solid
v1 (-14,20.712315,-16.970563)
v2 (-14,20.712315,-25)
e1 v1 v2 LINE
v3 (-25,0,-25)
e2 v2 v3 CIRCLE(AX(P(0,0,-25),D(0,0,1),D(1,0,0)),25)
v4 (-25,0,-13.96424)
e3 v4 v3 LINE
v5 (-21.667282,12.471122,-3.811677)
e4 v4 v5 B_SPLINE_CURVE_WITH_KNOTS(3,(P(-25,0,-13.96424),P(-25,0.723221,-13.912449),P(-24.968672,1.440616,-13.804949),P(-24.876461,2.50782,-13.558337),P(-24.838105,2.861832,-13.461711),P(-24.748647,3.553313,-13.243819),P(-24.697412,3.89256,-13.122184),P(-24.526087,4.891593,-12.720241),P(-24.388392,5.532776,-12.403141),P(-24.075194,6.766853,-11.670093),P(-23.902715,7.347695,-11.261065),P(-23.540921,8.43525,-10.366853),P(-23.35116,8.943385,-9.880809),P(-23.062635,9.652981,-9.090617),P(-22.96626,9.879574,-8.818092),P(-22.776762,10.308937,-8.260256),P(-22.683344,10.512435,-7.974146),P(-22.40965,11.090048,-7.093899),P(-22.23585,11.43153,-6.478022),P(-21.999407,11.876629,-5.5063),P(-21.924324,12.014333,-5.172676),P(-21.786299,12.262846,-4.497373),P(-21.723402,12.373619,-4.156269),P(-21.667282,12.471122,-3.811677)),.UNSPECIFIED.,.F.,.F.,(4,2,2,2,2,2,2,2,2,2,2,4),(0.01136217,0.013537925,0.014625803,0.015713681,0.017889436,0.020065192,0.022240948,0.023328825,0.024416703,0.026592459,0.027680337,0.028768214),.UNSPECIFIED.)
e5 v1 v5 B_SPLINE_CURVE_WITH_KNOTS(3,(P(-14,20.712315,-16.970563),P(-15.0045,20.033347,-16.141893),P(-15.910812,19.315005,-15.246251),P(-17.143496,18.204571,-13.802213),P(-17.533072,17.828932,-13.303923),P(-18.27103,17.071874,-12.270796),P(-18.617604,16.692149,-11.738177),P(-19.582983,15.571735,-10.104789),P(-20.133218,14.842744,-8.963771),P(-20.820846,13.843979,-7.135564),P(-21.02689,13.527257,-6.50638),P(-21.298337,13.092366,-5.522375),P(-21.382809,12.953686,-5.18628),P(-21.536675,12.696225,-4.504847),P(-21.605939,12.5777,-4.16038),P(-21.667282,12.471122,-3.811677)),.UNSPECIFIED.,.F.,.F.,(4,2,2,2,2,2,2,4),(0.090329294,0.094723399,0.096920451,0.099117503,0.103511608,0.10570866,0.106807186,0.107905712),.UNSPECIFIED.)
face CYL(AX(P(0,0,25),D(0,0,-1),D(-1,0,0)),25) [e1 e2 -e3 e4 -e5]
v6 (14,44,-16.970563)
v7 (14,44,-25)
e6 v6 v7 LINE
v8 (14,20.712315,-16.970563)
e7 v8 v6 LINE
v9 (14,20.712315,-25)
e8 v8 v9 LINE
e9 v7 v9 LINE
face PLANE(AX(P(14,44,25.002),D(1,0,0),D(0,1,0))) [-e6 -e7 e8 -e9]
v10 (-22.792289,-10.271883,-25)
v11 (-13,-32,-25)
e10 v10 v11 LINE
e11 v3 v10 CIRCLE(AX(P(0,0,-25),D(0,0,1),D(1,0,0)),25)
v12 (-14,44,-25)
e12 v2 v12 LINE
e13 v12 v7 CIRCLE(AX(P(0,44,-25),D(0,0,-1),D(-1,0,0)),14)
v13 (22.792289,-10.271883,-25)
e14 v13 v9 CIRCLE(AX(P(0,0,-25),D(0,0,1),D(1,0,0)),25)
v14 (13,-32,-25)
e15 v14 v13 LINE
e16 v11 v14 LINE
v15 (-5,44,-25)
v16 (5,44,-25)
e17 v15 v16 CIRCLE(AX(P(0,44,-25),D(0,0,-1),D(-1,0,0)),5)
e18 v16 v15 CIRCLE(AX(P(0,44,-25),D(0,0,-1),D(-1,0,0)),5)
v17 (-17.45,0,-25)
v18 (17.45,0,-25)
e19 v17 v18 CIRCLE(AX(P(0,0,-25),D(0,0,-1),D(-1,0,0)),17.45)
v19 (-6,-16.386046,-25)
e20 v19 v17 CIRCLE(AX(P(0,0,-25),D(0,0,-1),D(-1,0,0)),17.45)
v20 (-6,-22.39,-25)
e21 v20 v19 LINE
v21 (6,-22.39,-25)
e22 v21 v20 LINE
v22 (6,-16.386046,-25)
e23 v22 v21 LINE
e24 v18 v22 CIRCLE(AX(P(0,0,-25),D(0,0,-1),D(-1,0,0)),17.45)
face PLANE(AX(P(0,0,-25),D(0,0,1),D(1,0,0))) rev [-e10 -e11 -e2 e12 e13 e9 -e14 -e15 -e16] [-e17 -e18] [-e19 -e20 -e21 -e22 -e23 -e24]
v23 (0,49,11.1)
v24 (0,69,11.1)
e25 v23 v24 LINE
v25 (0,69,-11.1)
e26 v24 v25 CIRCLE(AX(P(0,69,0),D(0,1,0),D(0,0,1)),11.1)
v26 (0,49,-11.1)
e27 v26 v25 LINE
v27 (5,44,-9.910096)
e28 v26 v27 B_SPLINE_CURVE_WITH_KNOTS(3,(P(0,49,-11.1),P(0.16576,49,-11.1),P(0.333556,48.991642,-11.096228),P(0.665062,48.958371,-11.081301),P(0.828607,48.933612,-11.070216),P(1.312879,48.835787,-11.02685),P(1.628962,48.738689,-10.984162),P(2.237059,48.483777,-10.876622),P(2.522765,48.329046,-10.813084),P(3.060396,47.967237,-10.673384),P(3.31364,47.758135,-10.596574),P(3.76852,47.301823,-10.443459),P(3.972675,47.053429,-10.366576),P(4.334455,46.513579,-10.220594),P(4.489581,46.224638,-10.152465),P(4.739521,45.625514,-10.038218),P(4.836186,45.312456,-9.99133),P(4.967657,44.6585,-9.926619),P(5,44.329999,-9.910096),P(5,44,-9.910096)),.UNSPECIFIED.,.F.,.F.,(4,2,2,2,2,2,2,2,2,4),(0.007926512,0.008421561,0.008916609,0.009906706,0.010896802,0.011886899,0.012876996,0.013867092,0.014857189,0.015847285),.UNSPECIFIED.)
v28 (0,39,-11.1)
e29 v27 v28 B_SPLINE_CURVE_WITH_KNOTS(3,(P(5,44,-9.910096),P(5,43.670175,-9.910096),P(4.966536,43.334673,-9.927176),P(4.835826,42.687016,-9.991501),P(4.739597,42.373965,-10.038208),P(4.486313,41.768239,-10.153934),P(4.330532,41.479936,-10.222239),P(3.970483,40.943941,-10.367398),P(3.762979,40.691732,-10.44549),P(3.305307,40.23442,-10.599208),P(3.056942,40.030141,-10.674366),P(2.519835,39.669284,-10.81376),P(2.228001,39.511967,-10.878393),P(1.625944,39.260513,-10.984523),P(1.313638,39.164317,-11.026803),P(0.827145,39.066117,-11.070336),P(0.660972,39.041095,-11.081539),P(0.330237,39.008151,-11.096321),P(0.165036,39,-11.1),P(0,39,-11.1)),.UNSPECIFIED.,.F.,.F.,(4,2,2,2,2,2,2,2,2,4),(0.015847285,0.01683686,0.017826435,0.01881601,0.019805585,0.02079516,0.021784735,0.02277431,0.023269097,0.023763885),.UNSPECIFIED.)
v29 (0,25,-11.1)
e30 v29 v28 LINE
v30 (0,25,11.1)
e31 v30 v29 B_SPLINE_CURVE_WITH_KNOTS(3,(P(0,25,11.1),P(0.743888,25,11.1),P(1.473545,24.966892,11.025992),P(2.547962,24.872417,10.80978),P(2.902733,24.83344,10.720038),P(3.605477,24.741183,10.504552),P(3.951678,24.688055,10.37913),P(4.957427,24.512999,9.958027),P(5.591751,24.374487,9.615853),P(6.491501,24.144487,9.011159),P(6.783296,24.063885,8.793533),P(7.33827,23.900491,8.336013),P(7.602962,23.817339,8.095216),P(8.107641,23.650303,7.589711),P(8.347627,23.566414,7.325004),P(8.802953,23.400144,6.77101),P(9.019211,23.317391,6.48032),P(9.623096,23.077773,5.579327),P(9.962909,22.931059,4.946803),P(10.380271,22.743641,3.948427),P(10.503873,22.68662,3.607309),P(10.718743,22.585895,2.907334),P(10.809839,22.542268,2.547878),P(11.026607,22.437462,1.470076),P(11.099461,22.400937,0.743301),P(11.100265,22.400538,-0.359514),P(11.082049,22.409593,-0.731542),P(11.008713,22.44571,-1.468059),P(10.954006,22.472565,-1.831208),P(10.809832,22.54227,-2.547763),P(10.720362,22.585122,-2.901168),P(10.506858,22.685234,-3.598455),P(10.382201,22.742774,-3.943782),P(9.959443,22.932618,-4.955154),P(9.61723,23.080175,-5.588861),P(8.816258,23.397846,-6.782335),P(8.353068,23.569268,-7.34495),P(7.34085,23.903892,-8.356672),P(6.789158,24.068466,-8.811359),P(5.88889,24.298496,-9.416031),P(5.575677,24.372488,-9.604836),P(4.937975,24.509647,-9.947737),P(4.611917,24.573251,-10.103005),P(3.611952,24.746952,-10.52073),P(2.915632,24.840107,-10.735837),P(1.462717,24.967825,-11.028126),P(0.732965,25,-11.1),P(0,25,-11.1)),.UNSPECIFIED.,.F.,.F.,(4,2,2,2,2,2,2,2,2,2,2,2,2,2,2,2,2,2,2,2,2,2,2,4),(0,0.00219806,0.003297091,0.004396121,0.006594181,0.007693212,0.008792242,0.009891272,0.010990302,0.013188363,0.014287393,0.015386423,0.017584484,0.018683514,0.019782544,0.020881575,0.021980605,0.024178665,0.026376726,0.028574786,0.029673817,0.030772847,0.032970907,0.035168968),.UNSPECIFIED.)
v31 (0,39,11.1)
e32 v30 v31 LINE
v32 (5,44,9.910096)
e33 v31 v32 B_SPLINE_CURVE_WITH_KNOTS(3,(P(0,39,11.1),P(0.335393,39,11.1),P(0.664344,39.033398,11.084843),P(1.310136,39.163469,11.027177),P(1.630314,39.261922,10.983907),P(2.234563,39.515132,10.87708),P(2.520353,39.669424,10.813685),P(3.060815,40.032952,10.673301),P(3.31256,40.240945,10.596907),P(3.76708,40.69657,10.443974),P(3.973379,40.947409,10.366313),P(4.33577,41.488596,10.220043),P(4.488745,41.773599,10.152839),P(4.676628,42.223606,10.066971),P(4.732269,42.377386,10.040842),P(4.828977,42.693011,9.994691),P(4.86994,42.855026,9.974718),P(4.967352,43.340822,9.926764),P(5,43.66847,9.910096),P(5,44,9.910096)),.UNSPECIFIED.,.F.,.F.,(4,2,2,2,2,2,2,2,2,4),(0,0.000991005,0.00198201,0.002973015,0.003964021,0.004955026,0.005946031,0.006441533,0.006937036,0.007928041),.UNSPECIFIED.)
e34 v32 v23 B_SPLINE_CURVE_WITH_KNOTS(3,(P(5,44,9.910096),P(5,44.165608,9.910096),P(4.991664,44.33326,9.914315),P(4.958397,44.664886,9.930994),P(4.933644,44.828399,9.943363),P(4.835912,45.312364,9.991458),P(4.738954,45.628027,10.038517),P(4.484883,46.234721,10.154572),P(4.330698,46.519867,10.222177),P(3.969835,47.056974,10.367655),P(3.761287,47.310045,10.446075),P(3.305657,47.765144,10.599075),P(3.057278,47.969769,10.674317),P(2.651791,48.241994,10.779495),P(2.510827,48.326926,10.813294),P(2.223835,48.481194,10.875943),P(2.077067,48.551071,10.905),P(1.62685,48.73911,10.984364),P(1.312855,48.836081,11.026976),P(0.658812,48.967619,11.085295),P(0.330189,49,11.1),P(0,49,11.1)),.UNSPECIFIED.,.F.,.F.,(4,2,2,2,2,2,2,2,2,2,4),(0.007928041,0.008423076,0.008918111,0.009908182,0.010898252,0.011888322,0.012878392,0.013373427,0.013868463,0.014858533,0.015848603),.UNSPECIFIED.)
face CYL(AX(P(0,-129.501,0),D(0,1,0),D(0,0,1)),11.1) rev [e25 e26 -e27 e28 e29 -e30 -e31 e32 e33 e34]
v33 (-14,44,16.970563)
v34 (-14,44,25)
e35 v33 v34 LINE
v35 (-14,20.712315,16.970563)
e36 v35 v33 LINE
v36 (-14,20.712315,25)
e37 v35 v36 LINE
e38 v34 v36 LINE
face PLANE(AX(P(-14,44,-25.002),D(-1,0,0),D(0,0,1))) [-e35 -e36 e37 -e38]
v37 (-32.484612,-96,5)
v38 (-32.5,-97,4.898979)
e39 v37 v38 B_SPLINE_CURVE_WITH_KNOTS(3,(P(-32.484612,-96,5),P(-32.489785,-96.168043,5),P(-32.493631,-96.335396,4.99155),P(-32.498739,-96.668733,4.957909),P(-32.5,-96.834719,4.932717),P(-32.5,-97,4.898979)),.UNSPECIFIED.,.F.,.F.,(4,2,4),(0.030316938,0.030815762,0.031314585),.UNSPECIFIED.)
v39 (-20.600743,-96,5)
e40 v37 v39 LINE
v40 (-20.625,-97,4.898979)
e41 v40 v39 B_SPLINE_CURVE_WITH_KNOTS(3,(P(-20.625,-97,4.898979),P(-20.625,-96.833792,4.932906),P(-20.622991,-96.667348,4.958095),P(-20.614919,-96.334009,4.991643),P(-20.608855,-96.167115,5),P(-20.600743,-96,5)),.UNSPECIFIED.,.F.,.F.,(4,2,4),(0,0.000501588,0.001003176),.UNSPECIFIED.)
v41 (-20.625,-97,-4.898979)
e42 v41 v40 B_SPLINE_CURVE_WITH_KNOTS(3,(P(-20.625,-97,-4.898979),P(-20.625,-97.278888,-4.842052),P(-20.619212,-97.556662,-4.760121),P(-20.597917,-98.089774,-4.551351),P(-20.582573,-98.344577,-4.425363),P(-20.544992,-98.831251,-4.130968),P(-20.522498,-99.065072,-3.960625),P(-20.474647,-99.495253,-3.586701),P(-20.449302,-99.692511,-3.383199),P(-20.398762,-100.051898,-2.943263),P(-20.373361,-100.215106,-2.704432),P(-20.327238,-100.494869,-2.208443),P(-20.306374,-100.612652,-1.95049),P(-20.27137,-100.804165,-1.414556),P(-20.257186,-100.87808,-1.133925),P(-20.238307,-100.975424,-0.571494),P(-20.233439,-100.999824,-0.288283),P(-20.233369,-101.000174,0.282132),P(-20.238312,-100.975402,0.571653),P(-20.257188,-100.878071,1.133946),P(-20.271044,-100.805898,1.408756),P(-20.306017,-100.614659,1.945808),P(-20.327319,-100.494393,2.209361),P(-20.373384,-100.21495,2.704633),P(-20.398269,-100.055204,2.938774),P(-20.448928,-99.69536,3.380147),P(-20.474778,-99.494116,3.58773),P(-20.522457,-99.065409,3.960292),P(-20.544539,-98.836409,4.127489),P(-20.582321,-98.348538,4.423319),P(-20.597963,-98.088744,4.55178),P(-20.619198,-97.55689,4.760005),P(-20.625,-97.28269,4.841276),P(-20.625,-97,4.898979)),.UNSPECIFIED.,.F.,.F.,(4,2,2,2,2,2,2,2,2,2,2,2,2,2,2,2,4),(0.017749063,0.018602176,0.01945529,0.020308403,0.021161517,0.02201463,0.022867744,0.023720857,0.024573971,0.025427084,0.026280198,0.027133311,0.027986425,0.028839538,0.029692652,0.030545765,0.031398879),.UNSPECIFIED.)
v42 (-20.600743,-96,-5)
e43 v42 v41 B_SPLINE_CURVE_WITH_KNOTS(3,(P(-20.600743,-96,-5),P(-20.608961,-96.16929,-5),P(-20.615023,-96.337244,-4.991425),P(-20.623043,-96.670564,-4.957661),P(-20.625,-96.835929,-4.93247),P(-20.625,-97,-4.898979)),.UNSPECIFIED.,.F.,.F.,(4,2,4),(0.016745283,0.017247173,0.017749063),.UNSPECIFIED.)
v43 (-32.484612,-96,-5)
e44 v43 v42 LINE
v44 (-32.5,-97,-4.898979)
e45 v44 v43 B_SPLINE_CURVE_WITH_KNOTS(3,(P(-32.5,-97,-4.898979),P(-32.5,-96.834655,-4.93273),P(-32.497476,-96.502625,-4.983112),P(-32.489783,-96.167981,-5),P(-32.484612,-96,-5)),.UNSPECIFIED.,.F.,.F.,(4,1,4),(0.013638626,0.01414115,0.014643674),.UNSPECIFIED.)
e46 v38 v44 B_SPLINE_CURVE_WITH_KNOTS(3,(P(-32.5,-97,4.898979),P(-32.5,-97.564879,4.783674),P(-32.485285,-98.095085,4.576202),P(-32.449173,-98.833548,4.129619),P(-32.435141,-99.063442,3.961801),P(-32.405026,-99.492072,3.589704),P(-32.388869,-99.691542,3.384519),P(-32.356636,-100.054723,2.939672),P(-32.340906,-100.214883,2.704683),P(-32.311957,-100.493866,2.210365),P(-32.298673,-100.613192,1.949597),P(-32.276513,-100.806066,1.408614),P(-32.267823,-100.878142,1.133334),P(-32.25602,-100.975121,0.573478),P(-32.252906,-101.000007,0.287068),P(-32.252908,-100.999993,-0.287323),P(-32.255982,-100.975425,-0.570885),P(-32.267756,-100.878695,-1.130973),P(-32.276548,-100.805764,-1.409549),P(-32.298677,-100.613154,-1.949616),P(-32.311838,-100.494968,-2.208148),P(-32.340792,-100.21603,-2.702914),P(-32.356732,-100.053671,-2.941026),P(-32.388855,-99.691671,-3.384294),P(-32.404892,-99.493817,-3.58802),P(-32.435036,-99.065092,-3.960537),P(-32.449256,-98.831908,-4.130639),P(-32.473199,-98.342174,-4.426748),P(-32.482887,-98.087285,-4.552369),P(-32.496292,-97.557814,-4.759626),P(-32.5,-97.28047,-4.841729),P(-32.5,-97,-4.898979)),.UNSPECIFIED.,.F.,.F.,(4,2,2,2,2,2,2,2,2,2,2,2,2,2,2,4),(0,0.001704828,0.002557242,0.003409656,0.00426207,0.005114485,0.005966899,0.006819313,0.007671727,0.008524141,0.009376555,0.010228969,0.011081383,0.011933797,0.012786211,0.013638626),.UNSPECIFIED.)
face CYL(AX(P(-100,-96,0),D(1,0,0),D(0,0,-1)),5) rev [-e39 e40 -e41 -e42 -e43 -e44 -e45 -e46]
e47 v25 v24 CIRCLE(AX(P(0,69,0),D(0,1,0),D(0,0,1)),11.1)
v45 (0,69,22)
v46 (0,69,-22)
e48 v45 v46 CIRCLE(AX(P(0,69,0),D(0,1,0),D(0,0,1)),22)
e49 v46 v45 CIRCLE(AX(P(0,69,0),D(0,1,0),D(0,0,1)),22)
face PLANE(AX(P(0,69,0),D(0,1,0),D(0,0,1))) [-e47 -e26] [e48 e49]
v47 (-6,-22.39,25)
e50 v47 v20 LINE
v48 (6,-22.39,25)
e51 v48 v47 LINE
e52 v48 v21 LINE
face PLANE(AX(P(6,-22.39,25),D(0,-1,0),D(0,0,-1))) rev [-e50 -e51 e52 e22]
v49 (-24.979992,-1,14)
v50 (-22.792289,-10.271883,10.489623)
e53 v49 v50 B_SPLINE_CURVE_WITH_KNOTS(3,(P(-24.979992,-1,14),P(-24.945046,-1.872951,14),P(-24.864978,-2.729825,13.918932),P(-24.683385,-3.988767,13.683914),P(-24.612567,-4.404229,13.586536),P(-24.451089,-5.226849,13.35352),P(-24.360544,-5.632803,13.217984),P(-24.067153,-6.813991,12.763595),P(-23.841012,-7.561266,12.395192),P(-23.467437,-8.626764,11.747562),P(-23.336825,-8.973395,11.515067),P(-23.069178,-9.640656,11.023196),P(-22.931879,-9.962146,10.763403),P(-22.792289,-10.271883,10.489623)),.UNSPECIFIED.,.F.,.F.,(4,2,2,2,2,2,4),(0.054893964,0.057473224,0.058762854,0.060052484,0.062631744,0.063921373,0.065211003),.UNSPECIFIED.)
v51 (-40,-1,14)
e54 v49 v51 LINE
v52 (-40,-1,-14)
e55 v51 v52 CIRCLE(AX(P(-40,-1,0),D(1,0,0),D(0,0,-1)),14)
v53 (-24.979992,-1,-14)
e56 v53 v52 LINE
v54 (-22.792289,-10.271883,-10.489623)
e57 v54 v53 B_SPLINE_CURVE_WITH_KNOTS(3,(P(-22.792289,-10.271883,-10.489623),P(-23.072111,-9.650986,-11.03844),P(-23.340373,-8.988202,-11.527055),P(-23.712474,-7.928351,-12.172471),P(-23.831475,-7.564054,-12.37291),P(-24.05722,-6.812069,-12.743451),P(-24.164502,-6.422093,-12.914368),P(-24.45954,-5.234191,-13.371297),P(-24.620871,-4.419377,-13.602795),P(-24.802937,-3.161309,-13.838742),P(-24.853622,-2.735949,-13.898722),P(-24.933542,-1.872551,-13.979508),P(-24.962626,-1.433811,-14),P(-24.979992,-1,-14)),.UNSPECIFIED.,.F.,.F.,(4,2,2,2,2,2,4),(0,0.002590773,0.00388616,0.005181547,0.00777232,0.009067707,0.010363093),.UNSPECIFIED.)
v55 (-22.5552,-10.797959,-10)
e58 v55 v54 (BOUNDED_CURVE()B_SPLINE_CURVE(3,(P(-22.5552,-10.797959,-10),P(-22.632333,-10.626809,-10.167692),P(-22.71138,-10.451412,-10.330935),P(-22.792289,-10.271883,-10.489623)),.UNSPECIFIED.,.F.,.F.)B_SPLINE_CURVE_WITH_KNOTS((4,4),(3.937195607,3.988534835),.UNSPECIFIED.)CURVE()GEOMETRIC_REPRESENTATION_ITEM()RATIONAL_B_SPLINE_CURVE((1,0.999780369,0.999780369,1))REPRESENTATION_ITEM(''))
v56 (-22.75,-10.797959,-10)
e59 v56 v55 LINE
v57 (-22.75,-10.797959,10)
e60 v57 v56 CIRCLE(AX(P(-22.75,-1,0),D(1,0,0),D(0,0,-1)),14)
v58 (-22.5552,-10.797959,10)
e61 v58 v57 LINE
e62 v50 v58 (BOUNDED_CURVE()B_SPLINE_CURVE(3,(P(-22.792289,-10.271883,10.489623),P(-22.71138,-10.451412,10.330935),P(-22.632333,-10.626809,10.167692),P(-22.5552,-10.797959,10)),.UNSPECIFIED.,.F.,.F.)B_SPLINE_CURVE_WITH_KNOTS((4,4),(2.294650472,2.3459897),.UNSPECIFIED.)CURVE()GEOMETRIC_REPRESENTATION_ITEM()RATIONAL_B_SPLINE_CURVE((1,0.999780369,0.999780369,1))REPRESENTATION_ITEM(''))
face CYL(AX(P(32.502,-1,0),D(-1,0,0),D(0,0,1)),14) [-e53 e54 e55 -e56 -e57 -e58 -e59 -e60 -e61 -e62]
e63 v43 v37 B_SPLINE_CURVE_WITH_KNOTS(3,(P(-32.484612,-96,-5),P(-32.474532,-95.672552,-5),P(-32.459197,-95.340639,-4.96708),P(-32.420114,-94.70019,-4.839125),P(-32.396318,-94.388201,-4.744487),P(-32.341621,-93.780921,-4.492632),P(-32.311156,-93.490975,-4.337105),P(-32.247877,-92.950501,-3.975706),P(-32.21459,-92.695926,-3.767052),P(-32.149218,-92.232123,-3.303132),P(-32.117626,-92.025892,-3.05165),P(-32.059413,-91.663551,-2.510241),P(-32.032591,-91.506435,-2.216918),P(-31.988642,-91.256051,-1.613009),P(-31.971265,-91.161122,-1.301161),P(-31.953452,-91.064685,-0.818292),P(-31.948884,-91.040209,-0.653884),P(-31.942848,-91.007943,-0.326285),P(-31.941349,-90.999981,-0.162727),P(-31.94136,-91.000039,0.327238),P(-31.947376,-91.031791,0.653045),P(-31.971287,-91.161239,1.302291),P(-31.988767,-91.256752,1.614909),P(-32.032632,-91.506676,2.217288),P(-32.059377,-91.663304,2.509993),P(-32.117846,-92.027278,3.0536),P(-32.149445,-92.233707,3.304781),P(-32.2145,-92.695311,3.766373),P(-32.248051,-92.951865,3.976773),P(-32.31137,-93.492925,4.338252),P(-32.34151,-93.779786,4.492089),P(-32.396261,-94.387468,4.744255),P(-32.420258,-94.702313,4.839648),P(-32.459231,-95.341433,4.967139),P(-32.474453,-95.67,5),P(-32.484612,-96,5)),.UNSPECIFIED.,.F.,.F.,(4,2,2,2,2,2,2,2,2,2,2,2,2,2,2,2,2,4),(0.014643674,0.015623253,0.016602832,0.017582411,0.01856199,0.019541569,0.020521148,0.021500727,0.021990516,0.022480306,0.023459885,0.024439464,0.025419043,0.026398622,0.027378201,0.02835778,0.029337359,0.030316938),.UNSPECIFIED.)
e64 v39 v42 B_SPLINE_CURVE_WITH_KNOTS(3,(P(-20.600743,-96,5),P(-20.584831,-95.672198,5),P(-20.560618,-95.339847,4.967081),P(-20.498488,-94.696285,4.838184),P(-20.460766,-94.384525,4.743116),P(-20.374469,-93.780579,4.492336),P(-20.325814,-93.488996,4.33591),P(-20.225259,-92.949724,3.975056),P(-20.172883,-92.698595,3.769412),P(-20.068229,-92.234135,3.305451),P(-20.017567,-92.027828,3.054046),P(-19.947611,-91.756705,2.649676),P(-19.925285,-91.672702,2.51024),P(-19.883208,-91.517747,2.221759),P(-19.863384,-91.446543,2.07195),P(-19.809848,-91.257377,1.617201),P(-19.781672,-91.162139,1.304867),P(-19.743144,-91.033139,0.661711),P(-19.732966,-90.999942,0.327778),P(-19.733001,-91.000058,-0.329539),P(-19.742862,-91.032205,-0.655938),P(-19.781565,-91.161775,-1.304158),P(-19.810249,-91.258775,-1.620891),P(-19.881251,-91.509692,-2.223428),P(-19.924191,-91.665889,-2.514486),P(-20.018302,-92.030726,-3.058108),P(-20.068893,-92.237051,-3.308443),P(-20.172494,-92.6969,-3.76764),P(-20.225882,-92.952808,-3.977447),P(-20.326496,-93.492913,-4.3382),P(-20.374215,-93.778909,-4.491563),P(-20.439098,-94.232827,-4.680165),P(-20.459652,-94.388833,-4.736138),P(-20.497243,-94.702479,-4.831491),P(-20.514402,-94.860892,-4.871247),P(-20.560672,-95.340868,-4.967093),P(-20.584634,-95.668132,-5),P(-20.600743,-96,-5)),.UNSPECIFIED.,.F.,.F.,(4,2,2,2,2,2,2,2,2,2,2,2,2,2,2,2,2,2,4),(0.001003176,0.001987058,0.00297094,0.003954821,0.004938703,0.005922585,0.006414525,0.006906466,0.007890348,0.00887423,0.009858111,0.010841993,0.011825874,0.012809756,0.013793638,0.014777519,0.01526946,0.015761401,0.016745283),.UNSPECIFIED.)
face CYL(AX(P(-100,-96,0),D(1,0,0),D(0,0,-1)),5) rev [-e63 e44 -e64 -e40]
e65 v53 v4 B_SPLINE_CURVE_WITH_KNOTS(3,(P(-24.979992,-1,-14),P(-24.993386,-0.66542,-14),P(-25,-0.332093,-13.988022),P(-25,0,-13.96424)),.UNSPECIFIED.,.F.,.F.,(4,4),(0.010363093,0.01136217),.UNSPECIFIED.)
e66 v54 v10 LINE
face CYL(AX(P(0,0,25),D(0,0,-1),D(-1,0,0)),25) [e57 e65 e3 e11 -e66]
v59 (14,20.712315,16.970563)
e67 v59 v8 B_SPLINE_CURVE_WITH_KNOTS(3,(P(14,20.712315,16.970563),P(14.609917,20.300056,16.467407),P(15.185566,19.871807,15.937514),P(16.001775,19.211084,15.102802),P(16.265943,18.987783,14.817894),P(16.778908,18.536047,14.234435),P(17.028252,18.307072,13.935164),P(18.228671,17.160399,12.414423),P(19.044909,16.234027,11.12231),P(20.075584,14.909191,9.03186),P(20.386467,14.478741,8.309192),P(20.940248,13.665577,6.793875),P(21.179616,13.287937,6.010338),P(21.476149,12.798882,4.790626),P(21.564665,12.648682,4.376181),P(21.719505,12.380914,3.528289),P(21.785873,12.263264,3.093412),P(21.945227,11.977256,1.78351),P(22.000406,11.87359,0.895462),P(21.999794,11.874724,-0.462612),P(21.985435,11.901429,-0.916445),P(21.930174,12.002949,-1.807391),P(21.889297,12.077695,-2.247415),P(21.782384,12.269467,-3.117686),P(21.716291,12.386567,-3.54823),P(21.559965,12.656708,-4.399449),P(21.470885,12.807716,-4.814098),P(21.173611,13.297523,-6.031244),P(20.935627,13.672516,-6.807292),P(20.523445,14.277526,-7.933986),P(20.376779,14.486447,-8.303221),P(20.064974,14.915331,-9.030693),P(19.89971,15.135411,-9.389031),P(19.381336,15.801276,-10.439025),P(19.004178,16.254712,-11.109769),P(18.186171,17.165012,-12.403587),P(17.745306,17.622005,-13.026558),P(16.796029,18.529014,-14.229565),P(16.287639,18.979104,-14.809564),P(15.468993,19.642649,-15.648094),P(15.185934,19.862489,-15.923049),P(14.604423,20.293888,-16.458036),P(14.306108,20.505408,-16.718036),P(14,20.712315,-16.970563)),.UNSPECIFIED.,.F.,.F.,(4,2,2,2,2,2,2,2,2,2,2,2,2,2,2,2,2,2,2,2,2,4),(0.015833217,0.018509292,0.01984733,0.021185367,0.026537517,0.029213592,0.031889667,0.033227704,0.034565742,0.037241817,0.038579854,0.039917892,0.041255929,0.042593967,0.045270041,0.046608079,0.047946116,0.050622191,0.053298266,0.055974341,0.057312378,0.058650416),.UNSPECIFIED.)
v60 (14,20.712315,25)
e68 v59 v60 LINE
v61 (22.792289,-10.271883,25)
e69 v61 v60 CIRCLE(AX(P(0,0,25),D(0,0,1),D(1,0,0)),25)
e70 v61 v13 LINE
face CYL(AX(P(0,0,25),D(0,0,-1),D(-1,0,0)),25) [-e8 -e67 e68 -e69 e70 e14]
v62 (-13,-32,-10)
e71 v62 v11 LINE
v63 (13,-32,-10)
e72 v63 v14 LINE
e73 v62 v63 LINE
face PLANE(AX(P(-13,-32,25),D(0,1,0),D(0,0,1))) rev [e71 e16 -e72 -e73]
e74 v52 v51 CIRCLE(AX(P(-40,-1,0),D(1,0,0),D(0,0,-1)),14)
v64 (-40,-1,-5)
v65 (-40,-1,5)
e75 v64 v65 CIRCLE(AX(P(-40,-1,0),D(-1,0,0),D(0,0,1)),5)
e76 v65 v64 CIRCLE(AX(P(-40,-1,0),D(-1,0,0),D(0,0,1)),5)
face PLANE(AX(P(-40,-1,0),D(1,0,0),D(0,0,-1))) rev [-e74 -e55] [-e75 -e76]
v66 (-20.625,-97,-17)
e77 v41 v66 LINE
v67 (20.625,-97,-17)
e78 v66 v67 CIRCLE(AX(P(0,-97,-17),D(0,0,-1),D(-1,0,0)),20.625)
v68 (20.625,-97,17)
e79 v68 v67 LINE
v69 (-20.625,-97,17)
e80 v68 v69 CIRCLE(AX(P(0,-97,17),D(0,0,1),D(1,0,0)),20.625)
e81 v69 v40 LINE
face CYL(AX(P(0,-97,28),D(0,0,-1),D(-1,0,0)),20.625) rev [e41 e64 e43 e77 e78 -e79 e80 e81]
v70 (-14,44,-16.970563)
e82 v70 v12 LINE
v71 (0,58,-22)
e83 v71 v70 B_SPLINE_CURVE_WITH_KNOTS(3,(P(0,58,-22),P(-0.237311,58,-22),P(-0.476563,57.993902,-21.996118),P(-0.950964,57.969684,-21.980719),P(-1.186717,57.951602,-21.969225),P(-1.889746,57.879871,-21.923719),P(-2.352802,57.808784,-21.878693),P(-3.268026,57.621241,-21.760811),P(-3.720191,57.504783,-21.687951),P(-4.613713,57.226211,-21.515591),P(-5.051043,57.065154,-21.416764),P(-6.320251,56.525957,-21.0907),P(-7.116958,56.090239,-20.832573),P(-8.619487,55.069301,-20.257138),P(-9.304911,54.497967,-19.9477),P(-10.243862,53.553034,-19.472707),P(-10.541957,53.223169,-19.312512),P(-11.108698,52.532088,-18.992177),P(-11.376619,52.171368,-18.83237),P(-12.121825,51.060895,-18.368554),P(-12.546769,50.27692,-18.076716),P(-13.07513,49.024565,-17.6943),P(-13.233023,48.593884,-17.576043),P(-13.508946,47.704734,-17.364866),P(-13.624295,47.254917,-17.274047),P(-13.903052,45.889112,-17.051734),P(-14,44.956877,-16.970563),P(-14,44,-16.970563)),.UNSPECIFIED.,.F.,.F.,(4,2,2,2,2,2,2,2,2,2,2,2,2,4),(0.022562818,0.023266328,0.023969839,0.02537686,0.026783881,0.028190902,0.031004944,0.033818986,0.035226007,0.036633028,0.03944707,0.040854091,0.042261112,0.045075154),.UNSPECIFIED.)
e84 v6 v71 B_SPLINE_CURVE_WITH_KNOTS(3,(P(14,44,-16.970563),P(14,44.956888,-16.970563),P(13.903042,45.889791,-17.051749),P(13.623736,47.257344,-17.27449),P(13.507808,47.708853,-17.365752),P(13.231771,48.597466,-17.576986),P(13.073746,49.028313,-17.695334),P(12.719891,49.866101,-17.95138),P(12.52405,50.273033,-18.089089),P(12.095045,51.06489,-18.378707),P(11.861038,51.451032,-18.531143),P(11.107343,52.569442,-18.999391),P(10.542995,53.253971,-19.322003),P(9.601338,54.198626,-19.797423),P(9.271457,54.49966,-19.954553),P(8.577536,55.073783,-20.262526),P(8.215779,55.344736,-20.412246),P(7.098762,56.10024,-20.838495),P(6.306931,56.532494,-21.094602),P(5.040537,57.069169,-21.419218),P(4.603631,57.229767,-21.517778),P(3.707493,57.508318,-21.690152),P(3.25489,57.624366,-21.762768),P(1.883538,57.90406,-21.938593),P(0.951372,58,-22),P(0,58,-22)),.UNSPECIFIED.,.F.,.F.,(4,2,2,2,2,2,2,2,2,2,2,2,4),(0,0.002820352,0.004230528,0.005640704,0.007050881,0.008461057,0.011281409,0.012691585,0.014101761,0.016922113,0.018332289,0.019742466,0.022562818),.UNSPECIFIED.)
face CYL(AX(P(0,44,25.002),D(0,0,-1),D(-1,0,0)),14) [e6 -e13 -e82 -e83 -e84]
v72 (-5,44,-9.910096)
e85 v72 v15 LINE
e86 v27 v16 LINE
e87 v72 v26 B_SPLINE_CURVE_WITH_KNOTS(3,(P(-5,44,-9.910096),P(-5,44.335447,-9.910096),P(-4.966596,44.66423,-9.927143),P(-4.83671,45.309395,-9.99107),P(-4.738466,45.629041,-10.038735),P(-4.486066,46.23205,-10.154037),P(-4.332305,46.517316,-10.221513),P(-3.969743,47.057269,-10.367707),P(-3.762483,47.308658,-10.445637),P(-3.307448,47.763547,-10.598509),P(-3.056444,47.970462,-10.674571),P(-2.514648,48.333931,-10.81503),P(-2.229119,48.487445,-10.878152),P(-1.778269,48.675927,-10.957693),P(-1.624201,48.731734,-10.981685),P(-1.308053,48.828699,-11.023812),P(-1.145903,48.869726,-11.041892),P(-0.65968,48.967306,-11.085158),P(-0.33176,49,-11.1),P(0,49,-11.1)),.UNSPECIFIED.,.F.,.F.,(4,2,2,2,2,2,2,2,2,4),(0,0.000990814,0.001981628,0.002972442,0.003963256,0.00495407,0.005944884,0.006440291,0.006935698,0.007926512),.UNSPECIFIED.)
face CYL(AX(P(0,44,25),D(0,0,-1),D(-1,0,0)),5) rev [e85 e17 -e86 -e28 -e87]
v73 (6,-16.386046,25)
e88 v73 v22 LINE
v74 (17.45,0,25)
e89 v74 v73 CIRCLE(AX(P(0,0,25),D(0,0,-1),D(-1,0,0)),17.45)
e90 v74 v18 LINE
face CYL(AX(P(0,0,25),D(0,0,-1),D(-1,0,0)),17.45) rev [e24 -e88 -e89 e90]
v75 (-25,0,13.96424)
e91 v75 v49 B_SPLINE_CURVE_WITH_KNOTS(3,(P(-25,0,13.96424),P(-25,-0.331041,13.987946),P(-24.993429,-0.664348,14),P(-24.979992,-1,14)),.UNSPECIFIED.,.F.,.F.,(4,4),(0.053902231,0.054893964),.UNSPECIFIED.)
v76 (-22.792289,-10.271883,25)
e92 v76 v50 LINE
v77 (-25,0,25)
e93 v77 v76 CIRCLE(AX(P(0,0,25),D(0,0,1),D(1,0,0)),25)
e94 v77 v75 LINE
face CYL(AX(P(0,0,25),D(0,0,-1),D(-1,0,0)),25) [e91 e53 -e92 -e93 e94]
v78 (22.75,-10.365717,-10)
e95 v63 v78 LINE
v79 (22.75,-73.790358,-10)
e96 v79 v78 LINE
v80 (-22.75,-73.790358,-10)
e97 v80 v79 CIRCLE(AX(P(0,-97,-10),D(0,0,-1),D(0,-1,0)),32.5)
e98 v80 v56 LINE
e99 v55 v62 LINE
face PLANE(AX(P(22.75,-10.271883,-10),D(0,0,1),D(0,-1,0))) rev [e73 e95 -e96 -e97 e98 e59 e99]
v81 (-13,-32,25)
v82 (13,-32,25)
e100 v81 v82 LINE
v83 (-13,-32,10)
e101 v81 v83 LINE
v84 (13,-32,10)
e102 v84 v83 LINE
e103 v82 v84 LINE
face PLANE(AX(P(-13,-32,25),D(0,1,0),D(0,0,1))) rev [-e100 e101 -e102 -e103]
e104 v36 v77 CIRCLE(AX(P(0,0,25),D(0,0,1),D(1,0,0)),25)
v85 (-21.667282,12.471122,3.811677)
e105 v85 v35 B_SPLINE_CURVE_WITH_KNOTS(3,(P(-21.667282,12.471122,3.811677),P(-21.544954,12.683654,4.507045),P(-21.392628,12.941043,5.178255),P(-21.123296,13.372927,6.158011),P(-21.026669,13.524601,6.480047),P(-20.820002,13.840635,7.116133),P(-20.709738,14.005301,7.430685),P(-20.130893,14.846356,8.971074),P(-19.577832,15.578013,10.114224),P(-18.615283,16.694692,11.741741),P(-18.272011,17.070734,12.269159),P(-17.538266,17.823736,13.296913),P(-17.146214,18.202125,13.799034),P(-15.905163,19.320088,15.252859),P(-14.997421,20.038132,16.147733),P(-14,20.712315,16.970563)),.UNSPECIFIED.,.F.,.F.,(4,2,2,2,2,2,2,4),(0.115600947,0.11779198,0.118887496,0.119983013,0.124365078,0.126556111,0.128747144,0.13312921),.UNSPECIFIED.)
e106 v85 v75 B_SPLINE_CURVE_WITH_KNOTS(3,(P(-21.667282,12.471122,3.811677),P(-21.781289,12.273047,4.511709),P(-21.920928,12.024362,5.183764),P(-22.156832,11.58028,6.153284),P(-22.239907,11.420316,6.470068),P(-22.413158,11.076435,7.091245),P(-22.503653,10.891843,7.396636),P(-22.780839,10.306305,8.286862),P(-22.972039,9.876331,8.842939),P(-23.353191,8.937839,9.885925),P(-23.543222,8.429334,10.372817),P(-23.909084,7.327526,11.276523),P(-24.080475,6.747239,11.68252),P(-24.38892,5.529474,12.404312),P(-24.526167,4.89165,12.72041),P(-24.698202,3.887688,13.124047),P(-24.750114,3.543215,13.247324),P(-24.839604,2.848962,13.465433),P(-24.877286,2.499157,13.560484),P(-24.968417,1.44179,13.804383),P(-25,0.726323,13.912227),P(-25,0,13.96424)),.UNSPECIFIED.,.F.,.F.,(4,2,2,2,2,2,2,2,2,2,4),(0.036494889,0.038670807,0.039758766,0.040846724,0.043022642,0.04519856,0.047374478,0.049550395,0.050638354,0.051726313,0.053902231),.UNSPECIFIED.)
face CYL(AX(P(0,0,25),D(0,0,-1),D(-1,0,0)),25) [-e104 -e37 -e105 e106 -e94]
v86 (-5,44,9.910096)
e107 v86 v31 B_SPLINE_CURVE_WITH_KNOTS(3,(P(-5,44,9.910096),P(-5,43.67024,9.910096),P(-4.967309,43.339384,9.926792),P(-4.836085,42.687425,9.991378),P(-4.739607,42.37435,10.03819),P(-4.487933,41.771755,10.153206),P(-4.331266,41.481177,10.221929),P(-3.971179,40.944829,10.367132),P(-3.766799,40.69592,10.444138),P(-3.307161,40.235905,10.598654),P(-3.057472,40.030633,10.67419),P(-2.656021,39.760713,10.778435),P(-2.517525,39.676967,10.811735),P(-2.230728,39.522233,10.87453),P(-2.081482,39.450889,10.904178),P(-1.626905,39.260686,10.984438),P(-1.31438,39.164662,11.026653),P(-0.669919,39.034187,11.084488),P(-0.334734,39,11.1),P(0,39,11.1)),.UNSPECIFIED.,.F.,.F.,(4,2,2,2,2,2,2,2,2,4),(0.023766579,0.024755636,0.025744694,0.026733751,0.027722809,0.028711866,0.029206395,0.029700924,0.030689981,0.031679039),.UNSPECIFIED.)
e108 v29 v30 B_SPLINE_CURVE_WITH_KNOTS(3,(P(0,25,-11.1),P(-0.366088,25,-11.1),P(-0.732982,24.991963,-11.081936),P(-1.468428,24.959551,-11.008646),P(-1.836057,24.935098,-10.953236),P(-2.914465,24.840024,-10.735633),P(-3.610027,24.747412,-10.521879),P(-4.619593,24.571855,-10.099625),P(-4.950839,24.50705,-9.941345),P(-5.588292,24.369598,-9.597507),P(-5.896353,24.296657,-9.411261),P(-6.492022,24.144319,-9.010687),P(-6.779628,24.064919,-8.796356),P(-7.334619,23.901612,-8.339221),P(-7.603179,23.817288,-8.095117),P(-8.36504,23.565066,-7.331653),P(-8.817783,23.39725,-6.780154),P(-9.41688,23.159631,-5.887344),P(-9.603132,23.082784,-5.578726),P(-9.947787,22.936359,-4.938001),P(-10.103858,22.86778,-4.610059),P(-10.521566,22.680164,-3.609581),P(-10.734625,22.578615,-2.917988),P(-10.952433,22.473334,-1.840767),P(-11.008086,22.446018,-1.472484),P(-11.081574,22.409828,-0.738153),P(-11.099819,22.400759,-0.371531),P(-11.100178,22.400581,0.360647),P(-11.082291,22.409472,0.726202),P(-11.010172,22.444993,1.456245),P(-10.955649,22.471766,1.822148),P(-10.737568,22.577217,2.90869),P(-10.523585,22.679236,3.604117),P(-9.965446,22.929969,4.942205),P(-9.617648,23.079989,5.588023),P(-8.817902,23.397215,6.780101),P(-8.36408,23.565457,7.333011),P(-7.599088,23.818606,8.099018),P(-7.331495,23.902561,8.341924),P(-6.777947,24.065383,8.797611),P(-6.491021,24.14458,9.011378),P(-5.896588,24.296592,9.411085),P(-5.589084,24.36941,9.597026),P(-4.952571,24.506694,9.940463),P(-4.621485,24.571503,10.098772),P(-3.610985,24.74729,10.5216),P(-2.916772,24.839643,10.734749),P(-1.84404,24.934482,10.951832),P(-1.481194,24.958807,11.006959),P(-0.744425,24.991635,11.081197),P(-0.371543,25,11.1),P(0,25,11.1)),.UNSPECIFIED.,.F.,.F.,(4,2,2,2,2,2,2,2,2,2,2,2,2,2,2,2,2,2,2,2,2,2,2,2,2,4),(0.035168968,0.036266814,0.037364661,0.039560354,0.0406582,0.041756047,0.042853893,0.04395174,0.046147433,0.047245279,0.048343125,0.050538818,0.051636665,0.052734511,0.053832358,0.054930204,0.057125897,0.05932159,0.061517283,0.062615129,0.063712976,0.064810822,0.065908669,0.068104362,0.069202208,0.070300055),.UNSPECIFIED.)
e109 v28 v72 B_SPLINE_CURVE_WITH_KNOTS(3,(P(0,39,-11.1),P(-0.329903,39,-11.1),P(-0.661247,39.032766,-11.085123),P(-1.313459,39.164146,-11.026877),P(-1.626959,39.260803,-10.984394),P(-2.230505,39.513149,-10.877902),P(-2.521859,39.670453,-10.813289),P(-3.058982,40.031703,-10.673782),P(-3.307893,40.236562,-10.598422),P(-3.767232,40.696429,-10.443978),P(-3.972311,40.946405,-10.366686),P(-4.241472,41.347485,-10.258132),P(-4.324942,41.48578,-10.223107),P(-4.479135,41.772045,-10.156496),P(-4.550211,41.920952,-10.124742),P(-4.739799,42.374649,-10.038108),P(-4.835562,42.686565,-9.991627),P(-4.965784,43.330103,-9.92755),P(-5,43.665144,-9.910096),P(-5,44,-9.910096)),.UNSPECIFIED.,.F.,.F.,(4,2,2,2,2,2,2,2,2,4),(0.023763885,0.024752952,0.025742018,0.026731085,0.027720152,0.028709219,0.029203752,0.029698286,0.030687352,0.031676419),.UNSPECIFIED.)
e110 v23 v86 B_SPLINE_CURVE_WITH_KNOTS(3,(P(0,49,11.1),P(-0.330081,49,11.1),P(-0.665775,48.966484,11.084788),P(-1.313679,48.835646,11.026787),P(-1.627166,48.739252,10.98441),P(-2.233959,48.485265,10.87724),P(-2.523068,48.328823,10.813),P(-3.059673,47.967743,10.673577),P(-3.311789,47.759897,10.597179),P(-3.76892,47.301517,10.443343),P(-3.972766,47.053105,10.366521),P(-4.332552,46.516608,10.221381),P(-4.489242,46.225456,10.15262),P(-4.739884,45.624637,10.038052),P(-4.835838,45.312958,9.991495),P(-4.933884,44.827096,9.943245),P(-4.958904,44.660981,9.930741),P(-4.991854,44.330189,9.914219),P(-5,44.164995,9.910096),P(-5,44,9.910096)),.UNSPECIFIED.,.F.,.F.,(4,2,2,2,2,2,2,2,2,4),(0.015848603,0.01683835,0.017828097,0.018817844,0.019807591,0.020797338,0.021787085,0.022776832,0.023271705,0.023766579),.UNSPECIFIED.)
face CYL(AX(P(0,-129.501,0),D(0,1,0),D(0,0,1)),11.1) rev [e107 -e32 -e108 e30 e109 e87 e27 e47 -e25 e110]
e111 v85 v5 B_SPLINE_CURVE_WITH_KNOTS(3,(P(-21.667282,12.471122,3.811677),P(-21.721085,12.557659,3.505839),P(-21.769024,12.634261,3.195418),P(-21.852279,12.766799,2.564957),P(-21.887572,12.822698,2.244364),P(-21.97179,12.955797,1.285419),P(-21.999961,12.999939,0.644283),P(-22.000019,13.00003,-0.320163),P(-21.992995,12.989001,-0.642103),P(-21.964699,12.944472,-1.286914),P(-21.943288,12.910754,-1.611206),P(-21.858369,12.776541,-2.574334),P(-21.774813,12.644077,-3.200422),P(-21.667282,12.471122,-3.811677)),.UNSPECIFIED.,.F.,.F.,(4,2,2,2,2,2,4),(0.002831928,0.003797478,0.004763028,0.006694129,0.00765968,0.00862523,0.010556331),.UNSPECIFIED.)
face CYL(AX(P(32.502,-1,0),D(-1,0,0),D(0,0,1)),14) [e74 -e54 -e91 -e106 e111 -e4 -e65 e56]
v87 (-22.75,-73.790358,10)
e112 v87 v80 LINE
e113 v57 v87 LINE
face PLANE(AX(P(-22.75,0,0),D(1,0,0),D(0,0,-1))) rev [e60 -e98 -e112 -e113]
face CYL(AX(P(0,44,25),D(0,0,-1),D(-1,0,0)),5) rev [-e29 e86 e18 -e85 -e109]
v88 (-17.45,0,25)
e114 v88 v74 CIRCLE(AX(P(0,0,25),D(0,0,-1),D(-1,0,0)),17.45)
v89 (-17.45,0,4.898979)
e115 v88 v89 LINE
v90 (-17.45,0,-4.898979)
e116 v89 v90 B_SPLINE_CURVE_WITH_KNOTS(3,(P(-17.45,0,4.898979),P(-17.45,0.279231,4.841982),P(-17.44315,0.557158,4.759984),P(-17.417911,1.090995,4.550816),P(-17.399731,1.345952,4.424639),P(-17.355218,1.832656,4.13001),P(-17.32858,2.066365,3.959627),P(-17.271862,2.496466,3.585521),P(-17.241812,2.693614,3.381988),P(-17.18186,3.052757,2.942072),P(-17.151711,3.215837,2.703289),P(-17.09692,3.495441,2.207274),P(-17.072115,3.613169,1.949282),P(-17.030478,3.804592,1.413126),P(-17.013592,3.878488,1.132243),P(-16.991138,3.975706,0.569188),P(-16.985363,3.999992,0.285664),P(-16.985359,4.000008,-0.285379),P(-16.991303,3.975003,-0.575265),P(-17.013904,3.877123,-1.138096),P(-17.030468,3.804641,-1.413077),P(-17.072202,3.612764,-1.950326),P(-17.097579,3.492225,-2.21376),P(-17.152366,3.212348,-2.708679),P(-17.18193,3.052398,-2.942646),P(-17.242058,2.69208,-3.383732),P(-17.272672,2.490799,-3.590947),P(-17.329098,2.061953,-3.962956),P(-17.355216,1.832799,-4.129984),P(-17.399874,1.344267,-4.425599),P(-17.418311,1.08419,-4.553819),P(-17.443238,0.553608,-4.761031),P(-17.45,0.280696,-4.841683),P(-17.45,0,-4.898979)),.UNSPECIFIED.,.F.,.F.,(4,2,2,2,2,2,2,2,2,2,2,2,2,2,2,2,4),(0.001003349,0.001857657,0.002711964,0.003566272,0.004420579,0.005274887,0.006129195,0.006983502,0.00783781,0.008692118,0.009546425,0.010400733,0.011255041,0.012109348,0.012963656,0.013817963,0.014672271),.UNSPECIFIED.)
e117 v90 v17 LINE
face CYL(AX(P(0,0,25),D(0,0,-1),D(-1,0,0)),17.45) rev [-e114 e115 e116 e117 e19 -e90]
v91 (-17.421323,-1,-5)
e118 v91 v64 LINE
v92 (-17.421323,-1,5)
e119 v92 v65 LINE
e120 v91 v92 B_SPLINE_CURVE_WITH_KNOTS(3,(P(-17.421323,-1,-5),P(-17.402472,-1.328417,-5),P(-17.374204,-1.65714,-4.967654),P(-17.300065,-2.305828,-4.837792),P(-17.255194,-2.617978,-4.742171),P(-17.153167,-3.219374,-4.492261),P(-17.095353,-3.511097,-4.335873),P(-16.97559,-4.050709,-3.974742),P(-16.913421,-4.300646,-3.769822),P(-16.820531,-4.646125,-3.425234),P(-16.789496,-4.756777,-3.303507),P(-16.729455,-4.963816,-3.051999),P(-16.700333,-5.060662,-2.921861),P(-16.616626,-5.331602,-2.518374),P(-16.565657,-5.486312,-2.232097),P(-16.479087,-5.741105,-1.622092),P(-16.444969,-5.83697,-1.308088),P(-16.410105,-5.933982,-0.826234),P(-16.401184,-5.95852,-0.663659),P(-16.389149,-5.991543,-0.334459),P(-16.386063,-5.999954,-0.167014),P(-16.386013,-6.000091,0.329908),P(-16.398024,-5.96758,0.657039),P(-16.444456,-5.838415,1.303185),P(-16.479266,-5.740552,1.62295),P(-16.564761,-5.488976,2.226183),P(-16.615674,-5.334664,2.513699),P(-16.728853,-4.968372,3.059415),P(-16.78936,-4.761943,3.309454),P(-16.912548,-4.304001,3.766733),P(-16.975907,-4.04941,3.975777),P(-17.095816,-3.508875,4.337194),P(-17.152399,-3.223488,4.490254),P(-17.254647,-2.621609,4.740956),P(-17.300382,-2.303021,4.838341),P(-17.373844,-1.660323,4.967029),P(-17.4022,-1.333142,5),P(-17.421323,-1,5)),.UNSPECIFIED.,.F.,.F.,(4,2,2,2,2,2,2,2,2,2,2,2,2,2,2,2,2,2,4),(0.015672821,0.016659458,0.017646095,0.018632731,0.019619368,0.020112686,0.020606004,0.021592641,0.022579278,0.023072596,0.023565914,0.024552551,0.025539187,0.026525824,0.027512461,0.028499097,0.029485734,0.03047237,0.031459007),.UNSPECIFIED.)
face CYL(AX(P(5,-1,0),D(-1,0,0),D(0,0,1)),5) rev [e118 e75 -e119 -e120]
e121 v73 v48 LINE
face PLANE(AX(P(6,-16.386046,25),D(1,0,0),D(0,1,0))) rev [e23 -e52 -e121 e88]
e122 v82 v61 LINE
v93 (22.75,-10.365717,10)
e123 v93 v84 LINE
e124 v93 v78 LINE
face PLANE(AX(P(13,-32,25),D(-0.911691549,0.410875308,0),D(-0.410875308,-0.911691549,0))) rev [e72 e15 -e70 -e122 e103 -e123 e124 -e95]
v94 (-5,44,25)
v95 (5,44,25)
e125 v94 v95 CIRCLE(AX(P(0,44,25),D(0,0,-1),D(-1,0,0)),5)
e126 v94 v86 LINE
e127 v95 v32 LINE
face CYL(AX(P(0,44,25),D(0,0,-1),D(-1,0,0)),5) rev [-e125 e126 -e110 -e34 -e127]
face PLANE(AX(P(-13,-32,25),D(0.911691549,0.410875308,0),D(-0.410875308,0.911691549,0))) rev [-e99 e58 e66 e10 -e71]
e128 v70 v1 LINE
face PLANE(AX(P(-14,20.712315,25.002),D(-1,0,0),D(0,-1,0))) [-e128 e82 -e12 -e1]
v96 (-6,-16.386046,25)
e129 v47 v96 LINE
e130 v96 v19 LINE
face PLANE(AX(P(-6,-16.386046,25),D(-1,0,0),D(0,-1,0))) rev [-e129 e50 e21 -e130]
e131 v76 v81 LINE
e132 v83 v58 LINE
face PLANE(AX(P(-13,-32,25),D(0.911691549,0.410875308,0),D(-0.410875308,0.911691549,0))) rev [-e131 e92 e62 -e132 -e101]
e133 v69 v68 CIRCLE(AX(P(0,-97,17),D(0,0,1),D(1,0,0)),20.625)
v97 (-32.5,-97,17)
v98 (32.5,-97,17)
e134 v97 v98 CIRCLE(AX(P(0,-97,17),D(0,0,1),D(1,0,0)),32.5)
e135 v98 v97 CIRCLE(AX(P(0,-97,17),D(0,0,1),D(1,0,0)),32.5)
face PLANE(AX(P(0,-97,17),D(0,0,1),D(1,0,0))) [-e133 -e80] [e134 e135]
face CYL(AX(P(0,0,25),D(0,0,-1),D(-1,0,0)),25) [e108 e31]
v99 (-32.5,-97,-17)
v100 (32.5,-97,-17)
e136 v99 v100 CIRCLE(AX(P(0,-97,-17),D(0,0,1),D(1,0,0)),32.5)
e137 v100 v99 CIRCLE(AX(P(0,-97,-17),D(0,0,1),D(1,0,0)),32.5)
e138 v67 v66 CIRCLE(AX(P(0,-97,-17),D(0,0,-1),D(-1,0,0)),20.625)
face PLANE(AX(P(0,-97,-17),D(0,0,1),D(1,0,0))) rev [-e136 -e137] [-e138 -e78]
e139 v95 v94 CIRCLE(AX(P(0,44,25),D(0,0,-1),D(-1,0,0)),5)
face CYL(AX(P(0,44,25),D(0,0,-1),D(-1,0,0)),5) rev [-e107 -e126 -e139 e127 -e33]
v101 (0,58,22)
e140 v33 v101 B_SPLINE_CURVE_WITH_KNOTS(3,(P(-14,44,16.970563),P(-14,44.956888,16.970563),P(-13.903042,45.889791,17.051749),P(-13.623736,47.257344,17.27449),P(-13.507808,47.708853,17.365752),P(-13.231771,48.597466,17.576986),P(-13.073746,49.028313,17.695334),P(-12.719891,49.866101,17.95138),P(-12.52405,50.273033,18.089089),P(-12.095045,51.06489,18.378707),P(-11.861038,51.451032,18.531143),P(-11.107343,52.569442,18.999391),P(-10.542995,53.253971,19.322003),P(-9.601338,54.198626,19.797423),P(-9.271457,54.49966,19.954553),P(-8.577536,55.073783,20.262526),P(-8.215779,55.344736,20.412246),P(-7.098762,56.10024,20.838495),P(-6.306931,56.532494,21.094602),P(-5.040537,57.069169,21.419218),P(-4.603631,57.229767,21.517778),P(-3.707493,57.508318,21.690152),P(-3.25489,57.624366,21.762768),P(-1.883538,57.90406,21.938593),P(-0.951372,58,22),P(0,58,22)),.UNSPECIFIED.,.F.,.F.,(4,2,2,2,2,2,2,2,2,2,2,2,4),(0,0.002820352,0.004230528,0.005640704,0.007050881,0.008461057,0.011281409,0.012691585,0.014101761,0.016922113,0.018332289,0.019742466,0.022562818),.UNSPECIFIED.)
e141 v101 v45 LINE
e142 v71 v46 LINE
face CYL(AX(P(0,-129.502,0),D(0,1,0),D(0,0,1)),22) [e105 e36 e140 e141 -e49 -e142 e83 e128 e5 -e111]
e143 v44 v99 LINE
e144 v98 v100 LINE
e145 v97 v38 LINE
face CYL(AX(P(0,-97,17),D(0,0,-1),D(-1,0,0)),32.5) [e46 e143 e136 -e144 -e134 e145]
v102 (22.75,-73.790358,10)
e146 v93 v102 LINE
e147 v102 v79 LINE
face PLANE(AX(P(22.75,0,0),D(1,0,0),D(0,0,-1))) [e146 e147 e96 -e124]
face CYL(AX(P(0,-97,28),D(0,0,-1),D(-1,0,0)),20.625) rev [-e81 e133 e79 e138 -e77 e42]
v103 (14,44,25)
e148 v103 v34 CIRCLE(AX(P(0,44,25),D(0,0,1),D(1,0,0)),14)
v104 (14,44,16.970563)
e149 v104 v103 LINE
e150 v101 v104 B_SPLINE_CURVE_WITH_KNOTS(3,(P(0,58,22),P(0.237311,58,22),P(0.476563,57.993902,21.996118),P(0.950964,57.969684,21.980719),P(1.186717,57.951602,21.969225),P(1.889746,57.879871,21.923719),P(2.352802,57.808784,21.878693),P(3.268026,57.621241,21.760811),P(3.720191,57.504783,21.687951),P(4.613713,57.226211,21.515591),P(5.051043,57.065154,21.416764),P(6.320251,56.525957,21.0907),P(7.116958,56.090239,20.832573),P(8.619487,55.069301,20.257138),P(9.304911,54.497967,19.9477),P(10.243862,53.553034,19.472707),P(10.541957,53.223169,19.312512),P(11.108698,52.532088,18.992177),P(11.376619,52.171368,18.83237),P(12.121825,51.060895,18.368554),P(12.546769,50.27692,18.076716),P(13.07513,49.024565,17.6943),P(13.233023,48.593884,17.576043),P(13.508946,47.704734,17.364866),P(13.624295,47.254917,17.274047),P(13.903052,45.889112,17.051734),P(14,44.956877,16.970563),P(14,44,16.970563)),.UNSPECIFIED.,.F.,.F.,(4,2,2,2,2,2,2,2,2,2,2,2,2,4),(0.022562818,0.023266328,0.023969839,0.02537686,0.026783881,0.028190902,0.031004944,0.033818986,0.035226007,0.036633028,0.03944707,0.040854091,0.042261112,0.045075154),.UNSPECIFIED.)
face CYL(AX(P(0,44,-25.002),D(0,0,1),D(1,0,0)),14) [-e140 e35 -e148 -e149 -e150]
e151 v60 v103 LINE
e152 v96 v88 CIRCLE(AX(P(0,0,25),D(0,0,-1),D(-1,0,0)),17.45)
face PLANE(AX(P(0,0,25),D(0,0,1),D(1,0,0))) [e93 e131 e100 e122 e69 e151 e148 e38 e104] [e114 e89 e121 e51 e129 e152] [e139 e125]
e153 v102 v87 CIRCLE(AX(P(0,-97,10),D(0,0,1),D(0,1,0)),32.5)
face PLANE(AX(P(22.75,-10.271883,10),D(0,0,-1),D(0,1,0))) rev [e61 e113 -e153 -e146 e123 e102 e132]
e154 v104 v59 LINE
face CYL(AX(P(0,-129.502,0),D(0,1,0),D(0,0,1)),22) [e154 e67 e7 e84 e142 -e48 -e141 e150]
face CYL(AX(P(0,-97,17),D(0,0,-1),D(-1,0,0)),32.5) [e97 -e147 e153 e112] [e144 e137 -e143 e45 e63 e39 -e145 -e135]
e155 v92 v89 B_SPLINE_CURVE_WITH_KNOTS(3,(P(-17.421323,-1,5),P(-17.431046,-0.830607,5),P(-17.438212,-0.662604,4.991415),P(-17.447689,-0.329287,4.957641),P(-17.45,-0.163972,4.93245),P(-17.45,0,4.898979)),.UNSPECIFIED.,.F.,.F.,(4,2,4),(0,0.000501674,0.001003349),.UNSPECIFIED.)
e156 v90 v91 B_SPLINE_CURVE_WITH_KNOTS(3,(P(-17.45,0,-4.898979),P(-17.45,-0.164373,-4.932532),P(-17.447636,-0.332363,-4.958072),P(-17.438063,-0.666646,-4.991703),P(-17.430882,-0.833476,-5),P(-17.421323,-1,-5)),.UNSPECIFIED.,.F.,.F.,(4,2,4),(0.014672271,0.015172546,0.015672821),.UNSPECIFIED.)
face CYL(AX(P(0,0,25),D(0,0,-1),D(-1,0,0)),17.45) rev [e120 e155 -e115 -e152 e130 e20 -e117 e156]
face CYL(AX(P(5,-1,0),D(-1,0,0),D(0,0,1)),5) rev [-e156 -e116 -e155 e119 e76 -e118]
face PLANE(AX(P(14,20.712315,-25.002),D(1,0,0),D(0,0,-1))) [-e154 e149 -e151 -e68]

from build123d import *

# Parameters (mm, degrees)
CENTER_BLOCK_DEPTH             = 25
LOWER_EYE_PROFILE_65_R         = 32.5
LOWER_EYE_BOSS_65_DEPTH        = 17
CONNECTING_ARM_PROFILE_W       = 20
CONNECTING_ARM_PROFILE_H       = 65
CONNECTING_ARM_DEPTH           = 22.75
UPPER_BOSS_44_REACH            = 204.691
UPPER_BOSS_44_END_RADIUS       = 25
UPPER_BOSS_PROFILE_44_R        = 22
SIDE_PAD_REACH                 = 144.571
SIDE_PAD_END_RADIUS            = 22
SIDE_PAD_EXTENSION_REACH       = 144.571
UPPER_BORE_22_2_REACH          = 204.691
UPPER_BORE_22_2_END_RADIUS     = 25
UPPER_BORE_PROFILE_22_2_R      = 11.1
LUG_PLATE_REACH                = 152.504
LUG_PLATE_PROFILE_R            = 14
KEYED_SIDE_BORE_PROFILE_R      = 5
KEYED_SIDE_BORE_DEPTH          = 145.465393842
LUG_PIN_HOLE_PROFILE_10_R      = 5
LUG_PIN_HOLE_10_DEPTH          = 45
LOWER_EYE_BORE_PROFILE_41_25_R = 20.625
LOWER_EYE_BORE_41_25_DEPTH     = 45
CROSS_PIN_HOLE_PROFILE_10_R    = 5
CROSS_PIN_HOLE_10_DEPTH        = 100


with BuildPart() as part:
    # Center Block Profile → Center Block (new, symmetric)
    with BuildSketch(Plane.XY):
        with BuildLine():
            Line((-13, -32), (13, -32))
            Line((13, -32), (22.792288735, -10.271882702))
            ThreePointArc((22.792288735, -10.271882702), (0, 25), (-22.792288735, -10.271882702))
            Line((-22.792288735, -10.271882702), (-13, -32))
        make_face()
    extrude(amount=CENTER_BLOCK_DEPTH, both=True)



with BuildPart() as body_2:
    # Lower Eye Profile Ø65 → Lower Eye Boss Ø65 (new, symmetric)
    with BuildSketch(Plane.XY):
        with Locations((0, -97)):
            Circle(LOWER_EYE_PROFILE_65_R)
    extrude(amount=LOWER_EYE_BOSS_65_DEPTH, both=True)


with BuildPart() as part_1:
    add(part.part)

    add(body_2.part)  # Connecting Arm merges body 2
    # Connecting Arm Profile → Connecting Arm (add, symmetric)
    with BuildSketch(Plane(origin=(0, 0, 0), x_dir=(0, 0, -1), z_dir=(1, 0, 0))):
        with Locations((0, -42.771882702)):
            Rectangle(CONNECTING_ARM_PROFILE_W, CONNECTING_ARM_PROFILE_H)
    extrude(amount=CONNECTING_ARM_DEPTH, both=True)

    # Upper Boss Ø44: up to this cylinder (the profile starts outside it)
    upper_boss_44_end = Plane(origin=(0, 0, 0), z_dir=(0, 0, -1)) * Cylinder(UPPER_BOSS_44_END_RADIUS, 460.382, mode=Mode.PRIVATE)
    # Upper Boss Profile Ø44 → Upper Boss Ø44 (add, up to the surface)
    with BuildSketch(Plane(origin=(0, 69, 0), x_dir=(1, 0, 0), z_dir=(0, 1, 0)), mode=Mode.PRIVATE) as upper_boss_44_sk1:
        with Locations(Location((0, 0, 0), (0, 0, 270))):
            Circle(UPPER_BOSS_PROFILE_44_R)
    upper_boss_44_tool1 = extrude(upper_boss_44_sk1.sketch, amount=-UPPER_BOSS_44_REACH, mode=Mode.PRIVATE) - upper_boss_44_end
    add(upper_boss_44_tool1.solids().sort_by_distance((0, 69, 0))[0])

    # Side Pad: up to this cylinder (the profile starts outside it)
    side_pad_end = Plane(origin=(0, 39.439951, 0), z_dir=(0, 1, 0)) * Cylinder(SIDE_PAD_END_RADIUS, 334.142, mode=Mode.PRIVATE)
    # Side Pad Profile → Side Pad (add, up to the surface)
    with BuildSketch(Plane.XY.offset(25), mode=Mode.PRIVATE) as side_pad_sk1:
        with BuildLine():
            Line((-14, 44), (-14, 20.712315177))
            ThreePointArc((-14, 20.712315177), (0, 25), (14, 20.712315177))
            Line((14, 20.712315177), (14, 44))
            ThreePointArc((14, 44), (0, 58), (-14, 44))
        make_face()
    side_pad_tool1 = extrude(side_pad_sk1.sketch, amount=-SIDE_PAD_REACH, mode=Mode.PRIVATE) - side_pad_end
    add(side_pad_tool1.solids().sort_by_distance((0, 39.439951, 25))[0])

    # Side Pad Extension Profile → Side Pad Extension (add, up to next)
    with BuildSketch(Plane(origin=(0, 0, -25), x_dir=(-1, 0, 0), z_dir=(0, 0, -1)), mode=Mode.PRIVATE) as side_pad_extension_sk1:
        with BuildLine():
            Line((-14, 44), (-14, 20.712315177))
            ThreePointArc((-14, 20.712315177), (0, 25), (14, 20.712315177))
            Line((14, 20.712315177), (14, 44))
            ThreePointArc((14, 44), (0, 58), (-14, 44))
        make_face()
    side_pad_extension_tool1 = extrude(side_pad_extension_sk1.sketch, amount=-SIDE_PAD_EXTENSION_REACH, mode=Mode.PRIVATE) - part_1.part
    add(side_pad_extension_tool1.solids().sort_by_distance((0, 39.439951, -25))[0])

    # Upper Bore Ø22.2: up to this cylinder (the profile starts outside it)
    upper_bore_22_2_end = Plane(origin=(0, 0, 0), z_dir=(0, 0, -1)) * Cylinder(UPPER_BORE_22_2_END_RADIUS, 460.382, mode=Mode.PRIVATE)
    # Upper Bore Profile Ø22.2 → Upper Bore Ø22.2 (cut, up to the surface)
    with BuildSketch(Plane(origin=(0, 69, 0), x_dir=(1, 0, 0), z_dir=(0, 1, 0)), mode=Mode.PRIVATE) as upper_bore_22_2_sk1:
        with Locations(Location((0, 0, 0), (0, 0, 270))):
            Circle(UPPER_BORE_PROFILE_22_2_R)
    upper_bore_22_2_tool1 = extrude(upper_bore_22_2_sk1.sketch, amount=-UPPER_BORE_22_2_REACH, mode=Mode.PRIVATE) - upper_bore_22_2_end
    add(upper_bore_22_2_tool1.solids().sort_by_distance((0, 69, 0))[0], mode=Mode.SUBTRACT)

    # Lug Plate Profile → Lug Plate (add, up to next)
    with BuildSketch(Plane(origin=(-40, 0, 0), x_dir=(0, 0, -1), z_dir=(1, 0, 0)), mode=Mode.PRIVATE) as lug_plate_sk1:
        with Locations(Location((0, -1, 0), (0, 0, 221.473787501))):
            Circle(LUG_PLATE_PROFILE_R)
    lug_plate_tool1 = extrude(lug_plate_sk1.sketch, amount=LUG_PLATE_REACH, mode=Mode.PRIVATE) - part_1.part
    add(lug_plate_tool1.solids().sort_by_distance((-40, -1, 0))[0])

    # Keyed Side Bore Profile → Keyed Side Bore (cut, through all)
    with BuildSketch(Plane(origin=(0, 0, -25), x_dir=(-1, 0, 0), z_dir=(0, 0, -1))):
        with Locations((0, 44)):
            Circle(KEYED_SIDE_BORE_PROFILE_R)
        with BuildLine():
            Line((-6, -16.386045893), (-6, -22.39))
            Line((-6, -22.39), (6, -22.39))
            Line((6, -22.39), (6, -16.386045893))
            ThreePointArc((6, -16.386045893), (0, 17.45), (-6, -16.386045893))
        make_face()
    extrude(amount=-KEYED_SIDE_BORE_DEPTH, mode=Mode.SUBTRACT)

    # Lug Pin Hole Profile Ø10 → Lug Pin Hole Ø10 (cut)
    with BuildSketch(Plane.ZY.offset(40)):
        with Locations((0, -1)):
            Circle(LUG_PIN_HOLE_PROFILE_10_R)
    extrude(amount=-LUG_PIN_HOLE_10_DEPTH, mode=Mode.SUBTRACT)

    # Lower Eye Bore Profile Ø41.25 → Lower Eye Bore Ø41.25 (cut)
    with BuildSketch(Plane(origin=(0, 0, -17), x_dir=(-1, 0, 0), z_dir=(0, 0, -1))):
        with Locations((0, -97)):
            Circle(LOWER_EYE_BORE_PROFILE_41_25_R)
    extrude(amount=-LOWER_EYE_BORE_41_25_DEPTH, mode=Mode.SUBTRACT)

    # Cross Pin Hole Profile Ø10 → Cross Pin Hole Ø10 (cut)
    with BuildSketch(Plane(origin=(0, 0, 0), x_dir=(0, 0, -1), z_dir=(1, 0, 0))):
        with Locations(Location((0, -96, 0), (0, 0, 191.536959033))):
            Circle(CROSS_PIN_HOLE_PROFILE_10_R)
    extrude(amount=-CROSS_PIN_HOLE_10_DEPTH, mode=Mode.SUBTRACT)


solid = part_1.part
